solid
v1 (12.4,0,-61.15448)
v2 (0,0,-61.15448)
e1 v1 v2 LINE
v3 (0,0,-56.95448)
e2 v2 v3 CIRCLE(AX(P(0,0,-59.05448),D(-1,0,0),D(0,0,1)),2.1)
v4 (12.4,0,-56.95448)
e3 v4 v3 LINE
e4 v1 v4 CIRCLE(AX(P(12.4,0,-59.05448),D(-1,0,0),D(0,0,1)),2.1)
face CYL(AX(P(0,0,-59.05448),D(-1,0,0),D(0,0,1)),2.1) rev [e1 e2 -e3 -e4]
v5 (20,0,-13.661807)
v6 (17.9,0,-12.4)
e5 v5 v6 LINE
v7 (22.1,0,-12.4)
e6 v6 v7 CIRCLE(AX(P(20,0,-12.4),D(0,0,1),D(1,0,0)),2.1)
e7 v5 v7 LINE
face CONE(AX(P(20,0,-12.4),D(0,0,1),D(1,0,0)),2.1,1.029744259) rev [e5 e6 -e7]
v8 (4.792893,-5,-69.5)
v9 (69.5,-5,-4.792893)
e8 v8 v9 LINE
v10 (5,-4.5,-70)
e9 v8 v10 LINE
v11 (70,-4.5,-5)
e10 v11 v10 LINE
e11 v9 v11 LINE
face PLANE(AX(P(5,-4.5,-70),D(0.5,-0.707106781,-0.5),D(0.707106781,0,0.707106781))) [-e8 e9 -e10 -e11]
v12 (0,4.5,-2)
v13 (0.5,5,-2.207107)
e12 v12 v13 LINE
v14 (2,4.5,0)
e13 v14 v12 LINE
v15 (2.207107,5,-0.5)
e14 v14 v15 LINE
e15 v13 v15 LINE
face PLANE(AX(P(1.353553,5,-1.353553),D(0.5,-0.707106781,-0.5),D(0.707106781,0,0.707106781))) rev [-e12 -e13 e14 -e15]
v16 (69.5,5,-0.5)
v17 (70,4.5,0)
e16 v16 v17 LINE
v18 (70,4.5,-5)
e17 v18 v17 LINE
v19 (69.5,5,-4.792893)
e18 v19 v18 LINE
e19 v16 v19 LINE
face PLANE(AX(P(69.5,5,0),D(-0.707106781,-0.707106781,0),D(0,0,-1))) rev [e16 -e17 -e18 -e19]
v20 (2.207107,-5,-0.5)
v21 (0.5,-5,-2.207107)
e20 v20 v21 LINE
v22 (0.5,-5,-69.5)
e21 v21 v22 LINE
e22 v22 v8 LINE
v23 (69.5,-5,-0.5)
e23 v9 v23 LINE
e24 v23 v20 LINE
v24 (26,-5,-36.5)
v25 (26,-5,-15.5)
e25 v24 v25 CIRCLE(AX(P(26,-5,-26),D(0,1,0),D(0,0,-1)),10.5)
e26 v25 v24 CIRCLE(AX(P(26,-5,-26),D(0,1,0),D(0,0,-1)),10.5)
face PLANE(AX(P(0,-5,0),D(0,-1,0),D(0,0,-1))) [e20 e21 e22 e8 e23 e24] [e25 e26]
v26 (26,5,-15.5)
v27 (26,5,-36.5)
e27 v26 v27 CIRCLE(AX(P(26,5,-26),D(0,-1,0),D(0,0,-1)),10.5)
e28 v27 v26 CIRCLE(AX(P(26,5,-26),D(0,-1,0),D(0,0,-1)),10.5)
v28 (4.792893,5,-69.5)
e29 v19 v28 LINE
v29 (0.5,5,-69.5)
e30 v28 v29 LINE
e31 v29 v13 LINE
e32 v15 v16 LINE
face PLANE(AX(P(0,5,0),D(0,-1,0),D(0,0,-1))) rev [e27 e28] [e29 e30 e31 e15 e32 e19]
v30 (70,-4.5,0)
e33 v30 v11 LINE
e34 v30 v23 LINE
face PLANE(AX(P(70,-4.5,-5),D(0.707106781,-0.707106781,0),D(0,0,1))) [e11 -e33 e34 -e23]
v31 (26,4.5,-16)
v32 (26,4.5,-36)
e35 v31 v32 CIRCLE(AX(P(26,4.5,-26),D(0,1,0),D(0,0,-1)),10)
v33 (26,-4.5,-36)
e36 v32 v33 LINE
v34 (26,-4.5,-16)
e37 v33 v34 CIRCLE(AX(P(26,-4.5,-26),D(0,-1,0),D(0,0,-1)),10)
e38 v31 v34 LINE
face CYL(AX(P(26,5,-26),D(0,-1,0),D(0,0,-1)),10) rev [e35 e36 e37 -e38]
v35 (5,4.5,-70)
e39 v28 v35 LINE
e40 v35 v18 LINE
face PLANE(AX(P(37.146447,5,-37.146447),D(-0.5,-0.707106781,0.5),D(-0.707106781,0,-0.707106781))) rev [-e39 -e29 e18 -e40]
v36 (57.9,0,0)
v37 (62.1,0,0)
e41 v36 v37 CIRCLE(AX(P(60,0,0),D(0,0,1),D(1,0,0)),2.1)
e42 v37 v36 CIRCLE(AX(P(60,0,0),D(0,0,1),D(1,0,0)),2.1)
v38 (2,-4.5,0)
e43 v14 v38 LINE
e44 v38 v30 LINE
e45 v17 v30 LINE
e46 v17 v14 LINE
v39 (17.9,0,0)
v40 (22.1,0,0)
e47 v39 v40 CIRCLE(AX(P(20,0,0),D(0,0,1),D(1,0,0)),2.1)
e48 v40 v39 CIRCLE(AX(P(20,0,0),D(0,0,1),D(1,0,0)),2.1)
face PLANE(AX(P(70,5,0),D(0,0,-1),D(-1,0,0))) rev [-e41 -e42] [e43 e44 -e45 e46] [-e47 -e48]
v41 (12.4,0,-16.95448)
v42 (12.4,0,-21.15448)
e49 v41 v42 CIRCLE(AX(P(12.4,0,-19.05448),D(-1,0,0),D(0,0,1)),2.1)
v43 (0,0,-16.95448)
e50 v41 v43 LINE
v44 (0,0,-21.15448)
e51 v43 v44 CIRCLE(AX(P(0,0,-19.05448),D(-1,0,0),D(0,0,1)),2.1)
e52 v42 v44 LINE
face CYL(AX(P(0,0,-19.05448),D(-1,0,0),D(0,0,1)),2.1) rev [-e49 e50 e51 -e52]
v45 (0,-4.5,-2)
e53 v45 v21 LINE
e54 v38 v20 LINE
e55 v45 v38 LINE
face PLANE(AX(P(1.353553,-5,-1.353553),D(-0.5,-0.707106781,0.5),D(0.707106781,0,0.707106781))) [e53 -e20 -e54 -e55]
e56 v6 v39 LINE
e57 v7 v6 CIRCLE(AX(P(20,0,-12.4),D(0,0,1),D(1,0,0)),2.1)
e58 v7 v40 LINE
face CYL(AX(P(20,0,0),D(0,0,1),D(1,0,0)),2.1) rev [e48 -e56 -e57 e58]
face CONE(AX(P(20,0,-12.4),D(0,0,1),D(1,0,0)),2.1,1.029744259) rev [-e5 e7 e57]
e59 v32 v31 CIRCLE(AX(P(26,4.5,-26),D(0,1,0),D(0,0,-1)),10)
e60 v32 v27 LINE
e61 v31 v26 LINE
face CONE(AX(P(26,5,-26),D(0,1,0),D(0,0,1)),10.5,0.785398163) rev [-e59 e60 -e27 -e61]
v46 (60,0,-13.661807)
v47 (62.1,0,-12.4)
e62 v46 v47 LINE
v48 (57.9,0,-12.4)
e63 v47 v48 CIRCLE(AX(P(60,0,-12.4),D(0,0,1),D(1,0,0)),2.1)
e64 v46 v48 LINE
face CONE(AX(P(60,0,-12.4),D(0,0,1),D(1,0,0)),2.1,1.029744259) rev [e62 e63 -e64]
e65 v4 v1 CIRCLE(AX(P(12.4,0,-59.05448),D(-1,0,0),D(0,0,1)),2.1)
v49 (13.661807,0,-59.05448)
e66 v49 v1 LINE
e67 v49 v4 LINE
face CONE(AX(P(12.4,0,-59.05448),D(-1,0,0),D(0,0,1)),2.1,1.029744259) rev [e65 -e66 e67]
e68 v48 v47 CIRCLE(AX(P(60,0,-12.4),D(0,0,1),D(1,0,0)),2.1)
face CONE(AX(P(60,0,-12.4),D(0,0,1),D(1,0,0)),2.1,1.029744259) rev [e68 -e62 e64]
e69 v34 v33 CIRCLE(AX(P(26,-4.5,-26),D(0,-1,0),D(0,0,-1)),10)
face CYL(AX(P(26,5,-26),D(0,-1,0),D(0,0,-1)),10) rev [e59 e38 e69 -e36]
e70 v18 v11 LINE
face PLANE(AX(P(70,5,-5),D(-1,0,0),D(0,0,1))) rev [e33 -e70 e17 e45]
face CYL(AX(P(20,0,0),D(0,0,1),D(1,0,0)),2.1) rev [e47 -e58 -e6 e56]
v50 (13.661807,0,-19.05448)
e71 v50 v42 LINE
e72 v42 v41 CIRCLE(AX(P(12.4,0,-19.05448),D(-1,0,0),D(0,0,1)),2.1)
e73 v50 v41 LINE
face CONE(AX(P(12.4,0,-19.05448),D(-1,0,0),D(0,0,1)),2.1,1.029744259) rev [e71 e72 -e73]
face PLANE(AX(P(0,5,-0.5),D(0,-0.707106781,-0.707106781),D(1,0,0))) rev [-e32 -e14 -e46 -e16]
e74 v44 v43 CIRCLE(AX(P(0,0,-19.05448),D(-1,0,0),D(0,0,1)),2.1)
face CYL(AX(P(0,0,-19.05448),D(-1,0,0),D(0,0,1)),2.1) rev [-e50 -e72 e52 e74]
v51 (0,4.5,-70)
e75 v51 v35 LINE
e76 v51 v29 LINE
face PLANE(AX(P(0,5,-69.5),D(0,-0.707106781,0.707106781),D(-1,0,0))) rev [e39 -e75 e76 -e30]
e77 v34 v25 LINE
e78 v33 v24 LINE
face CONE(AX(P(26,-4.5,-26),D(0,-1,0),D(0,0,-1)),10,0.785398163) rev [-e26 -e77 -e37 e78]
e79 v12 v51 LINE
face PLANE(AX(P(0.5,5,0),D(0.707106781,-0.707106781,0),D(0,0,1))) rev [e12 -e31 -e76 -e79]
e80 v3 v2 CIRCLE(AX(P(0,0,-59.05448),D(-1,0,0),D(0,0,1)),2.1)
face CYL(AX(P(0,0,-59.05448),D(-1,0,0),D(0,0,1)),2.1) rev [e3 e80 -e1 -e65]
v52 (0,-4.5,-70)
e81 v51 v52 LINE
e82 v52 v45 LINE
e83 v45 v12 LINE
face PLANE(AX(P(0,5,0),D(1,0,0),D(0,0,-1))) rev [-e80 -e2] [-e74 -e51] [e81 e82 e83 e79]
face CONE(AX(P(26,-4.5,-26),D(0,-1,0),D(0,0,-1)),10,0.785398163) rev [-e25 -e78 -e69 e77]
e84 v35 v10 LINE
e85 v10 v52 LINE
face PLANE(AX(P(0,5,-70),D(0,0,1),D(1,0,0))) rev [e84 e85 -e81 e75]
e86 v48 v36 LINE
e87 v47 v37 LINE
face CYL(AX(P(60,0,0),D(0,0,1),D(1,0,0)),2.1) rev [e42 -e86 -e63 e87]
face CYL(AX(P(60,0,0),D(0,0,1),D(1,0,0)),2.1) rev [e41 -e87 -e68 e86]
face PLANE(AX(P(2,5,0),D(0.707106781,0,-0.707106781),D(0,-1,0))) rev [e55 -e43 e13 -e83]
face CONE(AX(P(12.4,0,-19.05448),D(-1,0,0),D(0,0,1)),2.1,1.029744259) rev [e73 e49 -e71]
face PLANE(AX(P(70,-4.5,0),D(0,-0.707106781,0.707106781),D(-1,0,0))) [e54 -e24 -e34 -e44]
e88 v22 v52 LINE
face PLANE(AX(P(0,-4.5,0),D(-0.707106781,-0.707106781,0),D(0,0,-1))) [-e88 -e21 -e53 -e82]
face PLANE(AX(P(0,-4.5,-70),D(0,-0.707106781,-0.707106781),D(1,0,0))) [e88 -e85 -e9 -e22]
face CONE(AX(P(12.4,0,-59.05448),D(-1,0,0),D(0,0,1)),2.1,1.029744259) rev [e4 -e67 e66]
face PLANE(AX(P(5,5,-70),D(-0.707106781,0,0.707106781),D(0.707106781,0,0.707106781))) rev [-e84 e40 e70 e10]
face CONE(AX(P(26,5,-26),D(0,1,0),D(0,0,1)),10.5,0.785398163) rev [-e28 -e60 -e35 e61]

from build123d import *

# Parameters (mm, degrees)
EXTRUDE_1_DEPTH        = 5
CHAMFER_1_SIZE         = 2
HOLE_WIZARD_M5_1_D     = 4.2
HOLE_WIZARD_M5_1_DEPTH = 12.4
HOLE_WIZARD_M5_1_TIP   = 1.2618073
HOLE_WIZARD_M5_2_D     = 4.2
HOLE_WIZARD_M5_2_DEPTH = 12.4
HOLE_WIZARD_M5_2_TIP   = 1.2618073
SKETCH_6_R             = 10
CUT_EXTRUDE_1_DEPTH    = 100.498743711
CHAMFER_2_SIZE         = 0.5


with BuildPart() as part:
    # 草图1 → 凸台-拉伸1 (new, symmetric)
    with BuildSketch(Plane(origin=(0, 0, 0), x_dir=(1, 0, 0), z_dir=(0, 1, 0))):
        Polygon((0, 0), (0, 70), (5, 70), (70, 5), (70, 0), align=None)
    extrude(amount=EXTRUDE_1_DEPTH, both=True)

    # 倒角1
    chamfer_1_edges = [part.edges().sort_by_distance(p)[0] for p in [
        (0, 0, 0),
    ]]
    chamfer(chamfer_1_edges, length=CHAMFER_1_SIZE)

    # M5 螺纹孔1
    with Locations(Plane.XY):
        with Locations((60, 0), (20, 0)):
            Hole(HOLE_WIZARD_M5_1_D / 2, depth=HOLE_WIZARD_M5_1_DEPTH)
            with Locations((0, 0, -(HOLE_WIZARD_M5_1_DEPTH + HOLE_WIZARD_M5_1_TIP / 2))):  # 118° drill point
                Cone(0, HOLE_WIZARD_M5_1_D / 2, HOLE_WIZARD_M5_1_TIP, mode=Mode.SUBTRACT)

    # M5 螺纹孔2
    with Locations(Plane.ZY):
        with Locations((-19.054479799, 0), (-59.054479799, 0)):
            Hole(HOLE_WIZARD_M5_2_D / 2, depth=HOLE_WIZARD_M5_2_DEPTH)
            with Locations((0, 0, -(HOLE_WIZARD_M5_2_DEPTH + HOLE_WIZARD_M5_2_TIP / 2))):  # 118° drill point
                Cone(0, HOLE_WIZARD_M5_2_D / 2, HOLE_WIZARD_M5_2_TIP, mode=Mode.SUBTRACT)

    # 草图6 → 切除-拉伸1 (cut, through all)
    with BuildSketch(Plane.XZ.offset(5)):
        with Locations(Location((26, -26, 0), (0, 0, 270))):
            Circle(SKETCH_6_R)
    extrude(amount=-CUT_EXTRUDE_1_DEPTH, mode=Mode.SUBTRACT)

    # 倒角2
    chamfer_2_edges = [part.edges().sort_by_distance(p)[0] for p in [
        (37.5, 5, -37.5),
        (2.5, 5, -70),
        (36, -5, 0),
        (0, 5, -36),
        (36, 5, 0),
        (1, -5, -1),
        (1, 5, -1),
        (26, 5, -16),
        (26, -5, -16),
        (0, -5, -36),
        (2.5, -5, -70),
        (37.5, -5, -37.5),
        (70, -5, -2.5),
        (70, 5, -2.5),
    ]]
    chamfer(chamfer_2_edges, length=CHAMFER_2_SIZE)


solid = part.part
